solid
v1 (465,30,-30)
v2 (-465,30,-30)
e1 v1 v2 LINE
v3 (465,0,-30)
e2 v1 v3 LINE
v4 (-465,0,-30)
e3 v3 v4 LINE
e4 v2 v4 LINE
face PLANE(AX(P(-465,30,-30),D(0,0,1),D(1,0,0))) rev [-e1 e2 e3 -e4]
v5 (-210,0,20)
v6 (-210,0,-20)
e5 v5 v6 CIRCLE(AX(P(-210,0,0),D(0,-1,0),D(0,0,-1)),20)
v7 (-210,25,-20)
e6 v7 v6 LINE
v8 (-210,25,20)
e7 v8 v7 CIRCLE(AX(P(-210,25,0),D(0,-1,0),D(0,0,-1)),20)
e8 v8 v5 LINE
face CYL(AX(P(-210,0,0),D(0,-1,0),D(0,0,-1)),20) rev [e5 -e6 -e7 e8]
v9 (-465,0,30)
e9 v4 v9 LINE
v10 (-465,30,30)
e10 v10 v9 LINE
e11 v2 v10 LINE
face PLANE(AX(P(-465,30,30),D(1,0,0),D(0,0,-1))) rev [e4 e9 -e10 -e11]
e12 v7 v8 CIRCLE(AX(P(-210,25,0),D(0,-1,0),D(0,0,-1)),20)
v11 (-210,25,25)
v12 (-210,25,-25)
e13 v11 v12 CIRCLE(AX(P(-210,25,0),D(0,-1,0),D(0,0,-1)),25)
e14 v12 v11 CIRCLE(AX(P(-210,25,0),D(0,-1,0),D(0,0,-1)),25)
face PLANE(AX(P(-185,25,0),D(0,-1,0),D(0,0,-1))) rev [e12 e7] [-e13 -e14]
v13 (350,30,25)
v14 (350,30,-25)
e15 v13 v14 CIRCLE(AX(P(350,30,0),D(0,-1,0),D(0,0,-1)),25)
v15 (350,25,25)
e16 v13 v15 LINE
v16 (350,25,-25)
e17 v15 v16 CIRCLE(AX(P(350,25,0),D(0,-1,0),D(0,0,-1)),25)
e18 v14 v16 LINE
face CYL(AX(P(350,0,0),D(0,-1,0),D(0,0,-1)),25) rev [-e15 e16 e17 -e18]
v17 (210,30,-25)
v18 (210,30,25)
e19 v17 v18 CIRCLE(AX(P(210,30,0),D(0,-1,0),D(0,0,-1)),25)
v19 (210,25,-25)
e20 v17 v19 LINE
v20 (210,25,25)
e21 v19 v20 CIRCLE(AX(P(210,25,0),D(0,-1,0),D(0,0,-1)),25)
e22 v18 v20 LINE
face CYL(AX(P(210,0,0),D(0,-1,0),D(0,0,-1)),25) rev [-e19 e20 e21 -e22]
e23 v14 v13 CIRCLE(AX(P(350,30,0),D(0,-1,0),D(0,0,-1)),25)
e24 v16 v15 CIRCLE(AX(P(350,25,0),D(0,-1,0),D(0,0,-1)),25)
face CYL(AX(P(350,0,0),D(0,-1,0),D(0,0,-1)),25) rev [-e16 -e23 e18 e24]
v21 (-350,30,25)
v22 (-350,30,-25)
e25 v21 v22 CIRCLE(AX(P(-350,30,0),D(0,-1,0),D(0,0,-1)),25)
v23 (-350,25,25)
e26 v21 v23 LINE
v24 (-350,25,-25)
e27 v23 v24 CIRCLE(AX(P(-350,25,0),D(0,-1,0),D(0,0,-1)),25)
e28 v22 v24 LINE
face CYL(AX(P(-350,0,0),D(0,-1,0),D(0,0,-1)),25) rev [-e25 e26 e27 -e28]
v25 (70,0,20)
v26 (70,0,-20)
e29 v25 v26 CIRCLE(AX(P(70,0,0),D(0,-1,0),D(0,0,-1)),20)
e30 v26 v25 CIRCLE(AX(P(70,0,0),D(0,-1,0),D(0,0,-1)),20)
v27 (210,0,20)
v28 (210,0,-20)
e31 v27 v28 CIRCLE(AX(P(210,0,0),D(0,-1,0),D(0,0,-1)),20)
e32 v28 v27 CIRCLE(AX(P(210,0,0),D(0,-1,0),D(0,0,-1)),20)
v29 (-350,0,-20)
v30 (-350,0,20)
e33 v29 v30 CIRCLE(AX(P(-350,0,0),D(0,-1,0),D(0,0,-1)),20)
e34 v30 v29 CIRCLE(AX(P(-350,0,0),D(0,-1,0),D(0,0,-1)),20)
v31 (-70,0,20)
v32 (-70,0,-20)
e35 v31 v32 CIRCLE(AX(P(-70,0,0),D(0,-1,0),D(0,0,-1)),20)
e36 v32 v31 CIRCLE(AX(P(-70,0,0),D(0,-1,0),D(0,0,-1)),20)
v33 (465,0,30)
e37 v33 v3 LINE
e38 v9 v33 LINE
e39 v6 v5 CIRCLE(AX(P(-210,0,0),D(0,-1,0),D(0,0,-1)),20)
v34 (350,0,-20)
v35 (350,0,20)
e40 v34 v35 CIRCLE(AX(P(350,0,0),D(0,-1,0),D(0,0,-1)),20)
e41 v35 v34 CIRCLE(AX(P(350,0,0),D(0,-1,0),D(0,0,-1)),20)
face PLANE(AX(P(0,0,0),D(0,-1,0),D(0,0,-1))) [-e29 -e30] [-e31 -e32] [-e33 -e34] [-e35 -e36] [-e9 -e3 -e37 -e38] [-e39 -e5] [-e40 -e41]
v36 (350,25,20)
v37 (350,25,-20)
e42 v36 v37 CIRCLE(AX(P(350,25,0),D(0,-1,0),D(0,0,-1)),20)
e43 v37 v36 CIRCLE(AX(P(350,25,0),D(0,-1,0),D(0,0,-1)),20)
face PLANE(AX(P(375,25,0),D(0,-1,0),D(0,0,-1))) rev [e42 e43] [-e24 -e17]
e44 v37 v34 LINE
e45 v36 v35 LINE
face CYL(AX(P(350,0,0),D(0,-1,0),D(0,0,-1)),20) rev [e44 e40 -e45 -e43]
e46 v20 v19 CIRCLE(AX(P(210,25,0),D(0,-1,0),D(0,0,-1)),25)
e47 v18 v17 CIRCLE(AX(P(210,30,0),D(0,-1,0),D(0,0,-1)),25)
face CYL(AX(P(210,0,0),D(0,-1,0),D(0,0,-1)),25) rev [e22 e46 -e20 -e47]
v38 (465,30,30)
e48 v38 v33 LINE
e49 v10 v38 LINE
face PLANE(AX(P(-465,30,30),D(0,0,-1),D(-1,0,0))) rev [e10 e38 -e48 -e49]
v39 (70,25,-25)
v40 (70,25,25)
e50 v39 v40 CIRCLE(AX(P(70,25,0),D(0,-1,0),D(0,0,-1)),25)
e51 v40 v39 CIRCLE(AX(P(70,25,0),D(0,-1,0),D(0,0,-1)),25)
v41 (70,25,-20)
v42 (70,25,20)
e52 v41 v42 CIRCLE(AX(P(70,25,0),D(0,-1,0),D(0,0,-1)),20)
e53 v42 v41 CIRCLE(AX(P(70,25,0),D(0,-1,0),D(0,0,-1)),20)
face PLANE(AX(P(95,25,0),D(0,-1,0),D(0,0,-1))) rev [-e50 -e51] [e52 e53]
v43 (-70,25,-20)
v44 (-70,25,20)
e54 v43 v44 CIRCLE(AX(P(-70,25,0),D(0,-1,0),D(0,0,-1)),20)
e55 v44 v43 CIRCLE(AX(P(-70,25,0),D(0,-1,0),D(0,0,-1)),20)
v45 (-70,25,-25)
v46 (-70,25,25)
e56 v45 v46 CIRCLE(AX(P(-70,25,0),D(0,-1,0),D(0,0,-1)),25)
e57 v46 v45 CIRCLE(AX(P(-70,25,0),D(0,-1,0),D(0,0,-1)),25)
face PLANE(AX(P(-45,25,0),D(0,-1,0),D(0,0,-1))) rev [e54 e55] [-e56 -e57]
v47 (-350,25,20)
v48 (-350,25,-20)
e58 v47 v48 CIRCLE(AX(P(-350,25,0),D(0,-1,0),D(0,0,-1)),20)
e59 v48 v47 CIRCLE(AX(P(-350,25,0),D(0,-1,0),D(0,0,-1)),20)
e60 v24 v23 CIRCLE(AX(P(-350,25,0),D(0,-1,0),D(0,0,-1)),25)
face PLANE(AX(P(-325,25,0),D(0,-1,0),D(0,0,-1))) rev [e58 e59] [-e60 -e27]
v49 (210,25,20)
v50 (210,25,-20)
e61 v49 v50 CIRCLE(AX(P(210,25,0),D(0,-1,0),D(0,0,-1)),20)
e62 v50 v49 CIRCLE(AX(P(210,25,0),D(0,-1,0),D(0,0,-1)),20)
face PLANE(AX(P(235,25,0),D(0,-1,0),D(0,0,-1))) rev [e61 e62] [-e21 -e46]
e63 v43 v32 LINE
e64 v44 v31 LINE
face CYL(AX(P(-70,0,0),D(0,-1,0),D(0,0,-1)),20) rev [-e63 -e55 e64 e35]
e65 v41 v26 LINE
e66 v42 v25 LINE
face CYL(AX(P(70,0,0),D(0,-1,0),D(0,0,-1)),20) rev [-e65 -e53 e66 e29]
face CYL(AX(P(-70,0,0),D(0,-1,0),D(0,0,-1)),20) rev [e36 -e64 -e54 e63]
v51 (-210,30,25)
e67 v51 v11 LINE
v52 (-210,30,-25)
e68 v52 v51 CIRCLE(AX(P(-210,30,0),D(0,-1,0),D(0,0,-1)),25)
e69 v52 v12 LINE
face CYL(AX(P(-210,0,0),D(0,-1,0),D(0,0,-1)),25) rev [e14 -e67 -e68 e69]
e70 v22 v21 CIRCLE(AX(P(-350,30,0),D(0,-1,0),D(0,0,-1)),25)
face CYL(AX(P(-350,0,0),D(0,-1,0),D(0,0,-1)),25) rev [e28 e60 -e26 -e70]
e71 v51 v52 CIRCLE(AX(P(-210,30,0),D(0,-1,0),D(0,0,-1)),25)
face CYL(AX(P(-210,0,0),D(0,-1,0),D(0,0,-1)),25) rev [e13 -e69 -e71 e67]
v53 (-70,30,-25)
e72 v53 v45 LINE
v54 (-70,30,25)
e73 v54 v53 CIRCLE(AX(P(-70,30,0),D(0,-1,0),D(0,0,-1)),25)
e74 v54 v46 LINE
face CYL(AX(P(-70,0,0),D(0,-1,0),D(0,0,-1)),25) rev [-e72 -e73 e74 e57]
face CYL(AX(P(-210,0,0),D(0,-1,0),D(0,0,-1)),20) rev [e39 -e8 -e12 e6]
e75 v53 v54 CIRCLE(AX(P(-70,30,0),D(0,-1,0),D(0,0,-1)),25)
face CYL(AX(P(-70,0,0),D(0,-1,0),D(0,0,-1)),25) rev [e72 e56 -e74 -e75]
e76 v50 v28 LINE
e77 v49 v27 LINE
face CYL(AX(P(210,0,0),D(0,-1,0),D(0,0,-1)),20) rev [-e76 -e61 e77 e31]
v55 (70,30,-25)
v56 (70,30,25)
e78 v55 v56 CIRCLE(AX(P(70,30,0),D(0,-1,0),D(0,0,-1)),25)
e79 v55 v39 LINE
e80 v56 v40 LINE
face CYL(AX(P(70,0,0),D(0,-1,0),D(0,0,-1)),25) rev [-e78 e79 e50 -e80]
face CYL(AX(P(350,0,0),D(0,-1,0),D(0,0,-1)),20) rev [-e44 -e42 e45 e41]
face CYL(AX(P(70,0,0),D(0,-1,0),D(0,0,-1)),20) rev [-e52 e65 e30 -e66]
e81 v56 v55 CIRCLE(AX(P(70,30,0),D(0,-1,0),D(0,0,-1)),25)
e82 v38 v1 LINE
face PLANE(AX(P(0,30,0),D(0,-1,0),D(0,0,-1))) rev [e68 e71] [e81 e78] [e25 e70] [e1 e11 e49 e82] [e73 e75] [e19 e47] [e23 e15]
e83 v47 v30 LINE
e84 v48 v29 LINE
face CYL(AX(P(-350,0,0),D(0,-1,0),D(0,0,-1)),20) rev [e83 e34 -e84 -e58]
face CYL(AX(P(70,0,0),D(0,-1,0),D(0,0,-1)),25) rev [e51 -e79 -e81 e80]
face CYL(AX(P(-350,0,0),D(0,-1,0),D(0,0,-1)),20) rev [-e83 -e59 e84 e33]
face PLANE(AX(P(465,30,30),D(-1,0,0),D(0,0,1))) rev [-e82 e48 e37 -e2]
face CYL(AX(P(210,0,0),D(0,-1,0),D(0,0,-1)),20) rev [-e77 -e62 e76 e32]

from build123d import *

# Parameters (mm, degrees)
SKETCH_1_W             = 930
SKETCH_1_H             = 60
EXTRUDE_1_DEPTH        = 30
PATTERN_LINEAR_1_COUNT = 6
PATTERN_LINEAR_1_PITCH = 140


with BuildPart() as part:
    # 草图1 → 凸台-拉伸1 (new body)
    with BuildSketch(Plane(origin=(0, 0, 0), x_dir=(1, 0, 0), z_dir=(0, 1, 0))):
        Rectangle(SKETCH_1_W, SKETCH_1_H)
    extrude(amount=EXTRUDE_1_DEPTH)

    # 草图3 → 切除-旋转1 (revolve, cut)
    with BuildSketch(Plane.XY, mode=Mode.PRIVATE) as cut_revolve_1_sk:
        Polygon((350, 30), (375, 30), (375, 25), (370, 25), (370, 0), (350, 0), align=None)
    cut_revolve_1 = revolve(cut_revolve_1_sk.sketch.rotate(Axis((350, 0, 0), (0, 1, 0)), 90), axis=Axis((350, 0, 0), (0, 1, 0)), mode=Mode.SUBTRACT)

    # 阵列(线性)1: 切除-旋转1 ×6
    with Locations(*[(-i * PATTERN_LINEAR_1_PITCH, 0, 0) for i in range(1, PATTERN_LINEAR_1_COUNT)]):
        add(cut_revolve_1, mode=Mode.SUBTRACT)


solid = part.part
